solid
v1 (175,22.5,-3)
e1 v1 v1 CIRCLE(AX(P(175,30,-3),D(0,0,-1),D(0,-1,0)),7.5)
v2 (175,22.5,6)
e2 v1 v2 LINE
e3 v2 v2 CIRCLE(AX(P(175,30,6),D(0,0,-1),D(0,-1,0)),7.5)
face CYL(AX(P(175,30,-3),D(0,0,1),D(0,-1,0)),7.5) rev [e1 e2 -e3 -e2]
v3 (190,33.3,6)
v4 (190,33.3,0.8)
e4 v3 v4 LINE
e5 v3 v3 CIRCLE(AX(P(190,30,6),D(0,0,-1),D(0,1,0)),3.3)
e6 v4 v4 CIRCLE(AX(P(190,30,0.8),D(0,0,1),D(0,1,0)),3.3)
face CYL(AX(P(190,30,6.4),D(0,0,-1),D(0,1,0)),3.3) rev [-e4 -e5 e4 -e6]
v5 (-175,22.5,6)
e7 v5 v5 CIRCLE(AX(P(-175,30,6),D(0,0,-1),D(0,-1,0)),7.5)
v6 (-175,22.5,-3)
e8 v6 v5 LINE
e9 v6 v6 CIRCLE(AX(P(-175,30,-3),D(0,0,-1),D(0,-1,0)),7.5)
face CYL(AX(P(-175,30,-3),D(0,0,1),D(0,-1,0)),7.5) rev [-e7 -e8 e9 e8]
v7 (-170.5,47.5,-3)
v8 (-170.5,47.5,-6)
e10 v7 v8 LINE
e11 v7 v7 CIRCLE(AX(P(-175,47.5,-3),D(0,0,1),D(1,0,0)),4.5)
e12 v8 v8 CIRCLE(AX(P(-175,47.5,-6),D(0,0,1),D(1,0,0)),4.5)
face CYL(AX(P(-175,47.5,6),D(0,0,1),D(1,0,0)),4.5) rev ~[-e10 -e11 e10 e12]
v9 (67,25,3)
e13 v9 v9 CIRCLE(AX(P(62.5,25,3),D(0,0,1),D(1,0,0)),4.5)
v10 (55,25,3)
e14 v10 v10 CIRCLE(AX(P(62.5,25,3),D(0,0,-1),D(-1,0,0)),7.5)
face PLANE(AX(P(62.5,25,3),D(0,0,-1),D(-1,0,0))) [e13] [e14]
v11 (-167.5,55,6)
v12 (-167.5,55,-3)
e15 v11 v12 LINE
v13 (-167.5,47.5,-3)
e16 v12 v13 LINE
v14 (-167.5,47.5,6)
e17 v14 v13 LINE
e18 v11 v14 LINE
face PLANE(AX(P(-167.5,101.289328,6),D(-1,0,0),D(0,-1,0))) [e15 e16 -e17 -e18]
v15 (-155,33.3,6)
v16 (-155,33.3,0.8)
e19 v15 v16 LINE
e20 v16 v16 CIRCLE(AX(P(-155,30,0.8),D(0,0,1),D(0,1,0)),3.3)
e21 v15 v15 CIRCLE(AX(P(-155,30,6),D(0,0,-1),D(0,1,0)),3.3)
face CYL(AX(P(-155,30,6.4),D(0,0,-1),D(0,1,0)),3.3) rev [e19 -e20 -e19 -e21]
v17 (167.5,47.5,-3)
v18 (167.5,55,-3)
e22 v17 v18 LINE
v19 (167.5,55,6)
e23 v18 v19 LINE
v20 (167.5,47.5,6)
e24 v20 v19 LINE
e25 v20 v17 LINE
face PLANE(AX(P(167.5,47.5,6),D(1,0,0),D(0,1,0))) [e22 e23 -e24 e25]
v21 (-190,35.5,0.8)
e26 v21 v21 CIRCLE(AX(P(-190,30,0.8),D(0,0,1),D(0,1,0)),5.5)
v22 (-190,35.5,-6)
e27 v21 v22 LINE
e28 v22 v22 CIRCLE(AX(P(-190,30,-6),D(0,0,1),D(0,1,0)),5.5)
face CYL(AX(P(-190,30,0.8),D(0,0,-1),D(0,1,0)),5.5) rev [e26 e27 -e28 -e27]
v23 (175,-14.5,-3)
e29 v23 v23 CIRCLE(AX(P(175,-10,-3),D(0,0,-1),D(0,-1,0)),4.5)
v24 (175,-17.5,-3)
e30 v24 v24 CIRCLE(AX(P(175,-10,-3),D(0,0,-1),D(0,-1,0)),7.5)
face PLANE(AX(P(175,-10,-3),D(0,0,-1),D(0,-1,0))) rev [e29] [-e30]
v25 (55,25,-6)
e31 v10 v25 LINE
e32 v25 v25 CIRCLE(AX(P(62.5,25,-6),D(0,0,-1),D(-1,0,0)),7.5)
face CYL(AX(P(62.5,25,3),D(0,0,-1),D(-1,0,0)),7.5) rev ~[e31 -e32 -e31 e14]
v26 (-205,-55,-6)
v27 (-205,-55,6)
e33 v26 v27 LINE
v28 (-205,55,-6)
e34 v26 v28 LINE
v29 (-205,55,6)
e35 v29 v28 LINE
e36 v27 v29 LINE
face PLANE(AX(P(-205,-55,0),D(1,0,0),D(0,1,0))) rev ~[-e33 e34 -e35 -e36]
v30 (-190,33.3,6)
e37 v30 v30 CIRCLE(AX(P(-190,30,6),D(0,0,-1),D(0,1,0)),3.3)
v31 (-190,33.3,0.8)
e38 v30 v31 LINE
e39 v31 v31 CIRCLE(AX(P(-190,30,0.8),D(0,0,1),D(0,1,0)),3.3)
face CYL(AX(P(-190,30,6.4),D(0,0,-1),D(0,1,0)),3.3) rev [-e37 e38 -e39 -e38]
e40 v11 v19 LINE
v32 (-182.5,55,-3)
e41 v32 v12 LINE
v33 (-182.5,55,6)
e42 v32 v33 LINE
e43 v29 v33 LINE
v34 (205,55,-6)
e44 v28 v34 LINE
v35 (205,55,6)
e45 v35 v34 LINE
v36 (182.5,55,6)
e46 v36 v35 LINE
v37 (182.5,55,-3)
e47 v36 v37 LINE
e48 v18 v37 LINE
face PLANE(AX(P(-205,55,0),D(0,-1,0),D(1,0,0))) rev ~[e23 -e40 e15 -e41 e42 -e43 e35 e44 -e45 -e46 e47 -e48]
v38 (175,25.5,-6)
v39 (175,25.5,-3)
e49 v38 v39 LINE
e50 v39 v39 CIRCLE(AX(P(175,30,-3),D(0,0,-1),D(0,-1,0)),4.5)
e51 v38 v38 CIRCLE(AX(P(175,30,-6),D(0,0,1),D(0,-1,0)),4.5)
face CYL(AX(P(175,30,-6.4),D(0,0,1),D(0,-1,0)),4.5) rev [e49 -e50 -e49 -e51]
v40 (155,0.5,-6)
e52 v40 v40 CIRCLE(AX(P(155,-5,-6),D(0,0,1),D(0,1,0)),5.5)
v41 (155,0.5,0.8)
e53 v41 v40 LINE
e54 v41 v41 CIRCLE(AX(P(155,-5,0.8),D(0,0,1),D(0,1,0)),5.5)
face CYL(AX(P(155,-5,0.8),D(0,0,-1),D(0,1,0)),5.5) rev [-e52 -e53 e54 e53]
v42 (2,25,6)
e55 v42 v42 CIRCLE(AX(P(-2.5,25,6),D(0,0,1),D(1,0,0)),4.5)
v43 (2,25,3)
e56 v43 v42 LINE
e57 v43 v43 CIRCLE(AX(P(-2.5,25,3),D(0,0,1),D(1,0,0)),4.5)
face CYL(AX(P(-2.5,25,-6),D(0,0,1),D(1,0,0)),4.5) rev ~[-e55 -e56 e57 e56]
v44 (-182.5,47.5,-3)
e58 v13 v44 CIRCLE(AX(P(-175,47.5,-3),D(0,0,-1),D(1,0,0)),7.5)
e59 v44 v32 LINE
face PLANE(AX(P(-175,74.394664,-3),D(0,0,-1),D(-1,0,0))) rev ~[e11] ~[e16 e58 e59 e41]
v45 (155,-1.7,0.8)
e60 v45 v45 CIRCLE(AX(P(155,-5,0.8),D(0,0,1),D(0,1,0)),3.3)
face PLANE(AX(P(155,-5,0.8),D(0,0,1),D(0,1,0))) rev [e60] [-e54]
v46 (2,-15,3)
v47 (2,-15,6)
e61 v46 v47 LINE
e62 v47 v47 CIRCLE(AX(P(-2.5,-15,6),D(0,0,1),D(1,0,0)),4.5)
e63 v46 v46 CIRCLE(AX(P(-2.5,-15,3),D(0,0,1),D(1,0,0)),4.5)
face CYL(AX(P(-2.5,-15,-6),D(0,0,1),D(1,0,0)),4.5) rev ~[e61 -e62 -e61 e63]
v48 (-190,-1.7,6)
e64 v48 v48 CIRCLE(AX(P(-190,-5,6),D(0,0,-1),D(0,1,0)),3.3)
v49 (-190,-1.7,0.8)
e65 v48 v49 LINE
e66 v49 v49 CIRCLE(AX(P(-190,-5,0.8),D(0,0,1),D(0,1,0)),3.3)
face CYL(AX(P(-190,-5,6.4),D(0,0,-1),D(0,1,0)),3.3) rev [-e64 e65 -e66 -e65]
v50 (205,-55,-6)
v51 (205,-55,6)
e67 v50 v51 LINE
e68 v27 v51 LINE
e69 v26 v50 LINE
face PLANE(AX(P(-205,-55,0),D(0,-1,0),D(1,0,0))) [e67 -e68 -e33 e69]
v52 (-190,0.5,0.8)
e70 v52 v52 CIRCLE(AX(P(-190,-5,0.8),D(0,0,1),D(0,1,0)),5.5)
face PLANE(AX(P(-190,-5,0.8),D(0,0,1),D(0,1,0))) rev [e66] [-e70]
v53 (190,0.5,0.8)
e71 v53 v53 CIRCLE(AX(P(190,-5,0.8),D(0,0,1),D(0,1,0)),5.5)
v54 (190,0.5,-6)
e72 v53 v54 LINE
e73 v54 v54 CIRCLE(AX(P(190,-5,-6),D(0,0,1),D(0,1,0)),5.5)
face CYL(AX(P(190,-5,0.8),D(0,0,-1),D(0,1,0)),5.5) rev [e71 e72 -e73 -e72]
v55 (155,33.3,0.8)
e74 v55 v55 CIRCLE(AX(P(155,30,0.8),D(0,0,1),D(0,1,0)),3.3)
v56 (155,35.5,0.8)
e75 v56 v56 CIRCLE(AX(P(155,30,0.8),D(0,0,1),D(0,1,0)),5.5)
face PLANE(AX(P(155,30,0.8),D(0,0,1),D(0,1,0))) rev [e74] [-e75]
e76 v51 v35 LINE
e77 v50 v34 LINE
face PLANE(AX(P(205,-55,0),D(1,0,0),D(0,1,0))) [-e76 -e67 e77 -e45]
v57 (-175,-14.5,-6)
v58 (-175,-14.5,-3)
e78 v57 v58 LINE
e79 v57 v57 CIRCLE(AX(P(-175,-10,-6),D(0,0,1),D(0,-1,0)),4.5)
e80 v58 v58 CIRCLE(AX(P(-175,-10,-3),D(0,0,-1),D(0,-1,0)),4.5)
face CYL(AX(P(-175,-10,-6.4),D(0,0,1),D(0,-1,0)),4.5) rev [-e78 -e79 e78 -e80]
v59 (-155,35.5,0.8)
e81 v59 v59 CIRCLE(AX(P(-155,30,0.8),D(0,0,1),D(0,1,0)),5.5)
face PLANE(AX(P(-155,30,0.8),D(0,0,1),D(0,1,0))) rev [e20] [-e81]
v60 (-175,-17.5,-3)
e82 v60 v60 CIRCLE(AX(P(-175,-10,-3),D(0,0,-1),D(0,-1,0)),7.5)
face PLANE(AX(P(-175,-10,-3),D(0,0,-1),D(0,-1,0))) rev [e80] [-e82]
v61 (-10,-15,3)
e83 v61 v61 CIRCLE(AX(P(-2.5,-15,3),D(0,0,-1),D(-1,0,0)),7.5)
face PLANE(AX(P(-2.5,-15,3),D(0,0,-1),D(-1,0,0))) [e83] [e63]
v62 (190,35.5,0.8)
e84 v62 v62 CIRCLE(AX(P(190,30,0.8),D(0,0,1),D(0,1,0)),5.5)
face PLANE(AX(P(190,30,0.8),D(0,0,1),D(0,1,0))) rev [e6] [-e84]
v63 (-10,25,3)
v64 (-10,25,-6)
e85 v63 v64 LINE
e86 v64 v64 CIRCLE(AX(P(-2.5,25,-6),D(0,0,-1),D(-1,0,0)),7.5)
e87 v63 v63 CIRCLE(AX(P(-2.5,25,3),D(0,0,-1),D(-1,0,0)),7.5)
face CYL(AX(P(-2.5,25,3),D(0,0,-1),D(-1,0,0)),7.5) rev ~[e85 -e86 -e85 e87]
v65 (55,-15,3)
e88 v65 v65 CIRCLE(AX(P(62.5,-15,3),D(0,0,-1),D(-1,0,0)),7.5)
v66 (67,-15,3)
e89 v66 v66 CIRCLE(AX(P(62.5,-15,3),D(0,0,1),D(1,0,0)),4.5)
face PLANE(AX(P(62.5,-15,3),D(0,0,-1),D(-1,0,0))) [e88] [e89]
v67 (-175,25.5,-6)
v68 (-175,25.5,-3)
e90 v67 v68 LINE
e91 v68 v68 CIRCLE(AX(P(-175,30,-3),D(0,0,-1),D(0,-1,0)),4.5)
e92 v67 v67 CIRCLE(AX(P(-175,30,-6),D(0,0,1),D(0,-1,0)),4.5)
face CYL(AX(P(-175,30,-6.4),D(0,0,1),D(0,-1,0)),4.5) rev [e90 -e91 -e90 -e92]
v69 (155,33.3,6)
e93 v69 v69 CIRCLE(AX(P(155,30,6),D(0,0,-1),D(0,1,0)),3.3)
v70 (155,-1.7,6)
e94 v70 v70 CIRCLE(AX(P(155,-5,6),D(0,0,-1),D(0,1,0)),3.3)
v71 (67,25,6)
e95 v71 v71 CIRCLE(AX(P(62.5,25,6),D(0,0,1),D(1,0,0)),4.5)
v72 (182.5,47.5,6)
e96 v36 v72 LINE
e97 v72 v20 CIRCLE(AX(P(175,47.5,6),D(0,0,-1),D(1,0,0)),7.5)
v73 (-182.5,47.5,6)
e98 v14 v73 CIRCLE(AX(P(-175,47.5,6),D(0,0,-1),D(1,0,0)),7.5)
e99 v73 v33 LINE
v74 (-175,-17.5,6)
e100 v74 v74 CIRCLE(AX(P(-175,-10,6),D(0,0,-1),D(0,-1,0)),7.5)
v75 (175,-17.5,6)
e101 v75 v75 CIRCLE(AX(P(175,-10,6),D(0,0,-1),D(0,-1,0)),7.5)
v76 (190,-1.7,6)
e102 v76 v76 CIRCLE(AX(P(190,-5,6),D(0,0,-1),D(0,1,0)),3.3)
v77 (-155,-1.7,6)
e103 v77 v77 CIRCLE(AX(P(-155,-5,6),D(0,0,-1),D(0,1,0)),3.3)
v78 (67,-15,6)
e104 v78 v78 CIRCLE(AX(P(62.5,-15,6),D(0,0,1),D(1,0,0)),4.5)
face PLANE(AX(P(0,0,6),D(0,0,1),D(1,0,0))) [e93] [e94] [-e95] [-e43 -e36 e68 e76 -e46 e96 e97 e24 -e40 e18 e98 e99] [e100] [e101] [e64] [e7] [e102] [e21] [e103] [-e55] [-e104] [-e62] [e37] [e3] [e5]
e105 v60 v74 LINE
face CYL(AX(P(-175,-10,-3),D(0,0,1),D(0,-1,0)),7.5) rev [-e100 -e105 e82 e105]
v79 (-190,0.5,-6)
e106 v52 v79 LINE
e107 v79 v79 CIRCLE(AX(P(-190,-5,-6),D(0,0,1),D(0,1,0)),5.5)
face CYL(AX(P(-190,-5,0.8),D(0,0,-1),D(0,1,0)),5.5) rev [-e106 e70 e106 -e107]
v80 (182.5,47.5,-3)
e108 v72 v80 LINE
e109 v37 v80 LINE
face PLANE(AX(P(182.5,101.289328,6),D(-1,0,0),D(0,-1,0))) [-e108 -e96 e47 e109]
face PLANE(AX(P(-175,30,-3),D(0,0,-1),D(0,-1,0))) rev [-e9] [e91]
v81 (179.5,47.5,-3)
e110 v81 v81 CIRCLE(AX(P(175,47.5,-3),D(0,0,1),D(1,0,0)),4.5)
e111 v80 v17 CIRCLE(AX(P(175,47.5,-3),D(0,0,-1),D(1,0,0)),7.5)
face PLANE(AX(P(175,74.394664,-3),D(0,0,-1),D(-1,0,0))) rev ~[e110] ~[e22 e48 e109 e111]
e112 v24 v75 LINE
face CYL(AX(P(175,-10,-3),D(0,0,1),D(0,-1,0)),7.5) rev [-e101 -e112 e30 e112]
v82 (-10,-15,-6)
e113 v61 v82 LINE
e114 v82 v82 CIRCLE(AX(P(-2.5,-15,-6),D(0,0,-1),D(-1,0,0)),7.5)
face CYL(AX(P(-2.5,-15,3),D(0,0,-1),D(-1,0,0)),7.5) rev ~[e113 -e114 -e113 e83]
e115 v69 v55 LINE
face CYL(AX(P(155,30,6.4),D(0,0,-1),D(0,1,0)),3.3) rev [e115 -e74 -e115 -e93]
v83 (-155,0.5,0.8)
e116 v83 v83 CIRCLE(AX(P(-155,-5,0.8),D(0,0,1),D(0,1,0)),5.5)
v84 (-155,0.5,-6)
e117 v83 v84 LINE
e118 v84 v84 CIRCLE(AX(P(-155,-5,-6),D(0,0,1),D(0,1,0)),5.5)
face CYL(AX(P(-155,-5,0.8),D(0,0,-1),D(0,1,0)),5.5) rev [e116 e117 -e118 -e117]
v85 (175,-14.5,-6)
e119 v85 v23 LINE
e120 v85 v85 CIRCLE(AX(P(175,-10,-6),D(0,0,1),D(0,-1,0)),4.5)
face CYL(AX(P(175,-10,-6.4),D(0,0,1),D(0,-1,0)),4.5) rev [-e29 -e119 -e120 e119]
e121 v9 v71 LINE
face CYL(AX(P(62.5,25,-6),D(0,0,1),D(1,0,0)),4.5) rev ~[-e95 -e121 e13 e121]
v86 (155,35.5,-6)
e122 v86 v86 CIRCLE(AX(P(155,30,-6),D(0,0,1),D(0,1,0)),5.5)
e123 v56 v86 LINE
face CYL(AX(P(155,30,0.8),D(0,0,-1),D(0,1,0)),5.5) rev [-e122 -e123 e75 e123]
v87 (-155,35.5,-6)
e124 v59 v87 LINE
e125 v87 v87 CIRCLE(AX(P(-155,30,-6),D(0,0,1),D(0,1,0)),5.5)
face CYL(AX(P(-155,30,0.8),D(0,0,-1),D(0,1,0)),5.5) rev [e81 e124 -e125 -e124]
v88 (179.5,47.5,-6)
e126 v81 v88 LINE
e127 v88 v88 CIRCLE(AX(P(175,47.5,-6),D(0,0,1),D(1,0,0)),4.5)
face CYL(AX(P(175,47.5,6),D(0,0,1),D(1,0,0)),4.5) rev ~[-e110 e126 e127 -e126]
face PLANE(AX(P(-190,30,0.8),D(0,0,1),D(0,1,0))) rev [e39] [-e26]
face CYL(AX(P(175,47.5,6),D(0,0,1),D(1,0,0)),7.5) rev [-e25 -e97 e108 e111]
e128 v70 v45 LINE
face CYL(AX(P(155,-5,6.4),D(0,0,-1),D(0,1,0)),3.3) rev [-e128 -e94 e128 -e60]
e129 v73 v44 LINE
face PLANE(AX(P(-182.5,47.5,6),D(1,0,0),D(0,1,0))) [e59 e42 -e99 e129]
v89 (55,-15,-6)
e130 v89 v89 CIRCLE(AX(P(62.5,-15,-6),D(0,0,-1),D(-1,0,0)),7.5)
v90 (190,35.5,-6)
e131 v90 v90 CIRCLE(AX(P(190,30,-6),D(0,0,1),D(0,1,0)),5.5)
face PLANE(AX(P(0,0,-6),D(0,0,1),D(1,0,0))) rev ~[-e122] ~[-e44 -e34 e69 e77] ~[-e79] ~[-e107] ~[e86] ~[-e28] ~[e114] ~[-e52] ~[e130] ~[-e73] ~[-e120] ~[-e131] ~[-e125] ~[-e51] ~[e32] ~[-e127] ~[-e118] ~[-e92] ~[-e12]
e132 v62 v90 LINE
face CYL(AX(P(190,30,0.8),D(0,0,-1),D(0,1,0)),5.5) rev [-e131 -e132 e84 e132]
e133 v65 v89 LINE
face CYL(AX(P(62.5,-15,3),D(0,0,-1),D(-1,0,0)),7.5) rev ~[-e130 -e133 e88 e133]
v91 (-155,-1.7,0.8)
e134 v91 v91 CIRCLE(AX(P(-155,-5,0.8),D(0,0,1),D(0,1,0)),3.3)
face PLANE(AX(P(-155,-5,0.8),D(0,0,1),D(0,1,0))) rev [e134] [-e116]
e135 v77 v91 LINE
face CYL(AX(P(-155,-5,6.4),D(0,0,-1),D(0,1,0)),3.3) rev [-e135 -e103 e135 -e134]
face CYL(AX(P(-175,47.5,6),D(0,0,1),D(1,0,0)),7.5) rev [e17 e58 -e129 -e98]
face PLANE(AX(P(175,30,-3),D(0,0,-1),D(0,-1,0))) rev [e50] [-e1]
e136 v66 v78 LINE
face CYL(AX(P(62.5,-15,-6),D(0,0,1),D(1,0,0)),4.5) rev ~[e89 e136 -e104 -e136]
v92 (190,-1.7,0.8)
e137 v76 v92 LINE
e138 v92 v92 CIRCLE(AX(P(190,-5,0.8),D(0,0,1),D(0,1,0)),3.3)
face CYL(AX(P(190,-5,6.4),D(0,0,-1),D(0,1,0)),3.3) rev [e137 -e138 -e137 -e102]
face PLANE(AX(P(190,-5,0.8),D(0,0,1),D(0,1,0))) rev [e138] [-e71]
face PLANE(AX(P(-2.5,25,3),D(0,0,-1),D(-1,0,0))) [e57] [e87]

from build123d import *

# Parameters (mm, degrees)
SKETCH_1_W                 = 410
SKETCH_1_H                 = 110
EXTRUDE_1_DEPTH            = 6
HOLE_WIZARD_3_AT_2_COUNT   = 2
HOLE_WIZARD_3_AT_2_PITCH   = 35
HOLE_WIZARD_3_AT_3_COUNT   = 2
HOLE_WIZARD_3_AT_3_PITCH   = 35
HOLE_WIZARD_3_AT_4_COUNT   = 2
HOLE_WIZARD_3_AT_4_PITCH   = 49.497474683
PATTERN_LINEAR_1_COUNT     = 2
PATTERN_LINEAR_1_PITCH     = 345
HOLE_WIZARD_2_D            = 9
HOLE_WIZARD_2_DEPTH        = 12.4
HOLE_WIZARD_2_CBORE_D      = 15
HOLE_WIZARD_2_CBORE_DEPTH  = 9
HOLE_WIZARD_2_TIP          = 2.703872786
HOLE_WIZARD_3_2_AT_2_COUNT = 2
HOLE_WIZARD_3_2_AT_2_PITCH = 40
SKETCH_14_R                = 4.5
CUT_EXTRUDE_1_DEPTH        = 213.588804973
CUT_EXTRUDE_2_DEPTH        = 9
PATTERN_LINEAR_2_COUNT     = 2
PATTERN_LINEAR_2_PITCH     = 350


with BuildPart() as part:
    # 草图1 → 凸台-拉伸1 (new, symmetric)
    with BuildSketch(Plane.XY):
        Rectangle(SKETCH_1_W, SKETCH_1_H)
    extrude(amount=EXTRUDE_1_DEPTH, both=True)

    # 草图3 → Hole Wizard 3 (revolve, cut)
    with BuildSketch(Plane(origin=(190, 30, -6), x_dir=(0, 1, 0), z_dir=(1, 0, 0))):
        Polygon((0, 0), (0, 14.382840043), (3.3, 12.4), (3.3, 6.8), (5.5, 6.8), (5.5, 0), align=None)
    hole_wizard_3 = revolve(axis=Axis((190, 30, -12.35), (0, 0, 1)), mode=Mode.SUBTRACT)

    # Hole Wizard 3 at 2: Hole Wizard 3 ×2
    with Locations(*[(-i * HOLE_WIZARD_3_AT_2_PITCH, 0, 0) for i in range(1, HOLE_WIZARD_3_AT_2_COUNT)]):
        add(hole_wizard_3, mode=Mode.SUBTRACT)

    # Hole Wizard 3 at 3: Hole Wizard 3 ×2
    with Locations(*[(0, -i * HOLE_WIZARD_3_AT_3_PITCH, 0) for i in range(1, HOLE_WIZARD_3_AT_3_COUNT)]):
        add(hole_wizard_3, mode=Mode.SUBTRACT)

    # Hole Wizard 3 at 4: Hole Wizard 3 ×2
    with Locations(*[Vector(-0.7071067811865477, -0.7071067811865474, 0) * (i * HOLE_WIZARD_3_AT_4_PITCH) for i in range(1, HOLE_WIZARD_3_AT_4_COUNT)]):
        add(hole_wizard_3, mode=Mode.SUBTRACT)

    # 阵列(线性)1: Hole Wizard 3 ×2
    with Locations(*[(-i * PATTERN_LINEAR_1_PITCH, 0, 0) for i in range(1, PATTERN_LINEAR_1_COUNT)]):
        add(hole_wizard_3, mode=Mode.SUBTRACT)

    # 阵列(线性)1 copy 1 sketch → 阵列(线性)1 copy 1 (revolve, cut)
    with BuildSketch(Plane(origin=(-190, 30, -6), x_dir=(0, 1, 0), z_dir=(1, 0, 0))):
        Polygon((0, 0), (0, 14.382840043), (3.3, 12.4), (3.3, 6.8), (5.5, 6.8), (5.5, 0), align=None)
    revolve(axis=Axis((-190, 30, -12.35), (0, 0, 1)), mode=Mode.SUBTRACT)

    # 阵列(线性)1 copy 2 sketch → 阵列(线性)1 copy 2 (revolve, cut)
    with BuildSketch(Plane(origin=(-155, -5, -6), x_dir=(0, 1, 0), z_dir=(1, 0, 0))):
        Polygon((0, 0), (0, 14.382840043), (3.3, 12.4), (3.3, 6.8), (5.5, 6.8), (5.5, 0), align=None)
    revolve(axis=Axis((-155, -5, -12.35), (0, 0, 1)), mode=Mode.SUBTRACT)

    # 阵列(线性)1 copy 3 sketch → 阵列(线性)1 copy 3 (revolve, cut)
    with BuildSketch(Plane(origin=(-190, -5, -6), x_dir=(0, 1, 0), z_dir=(1, 0, 0))):
        Polygon((0, 0), (0, 14.382840043), (3.3, 12.4), (3.3, 6.8), (5.5, 6.8), (5.5, 0), align=None)
    revolve(axis=Axis((-190, -5, -12.35), (0, 0, 1)), mode=Mode.SUBTRACT)

    # 打孔尺寸(%根据)内六角圆柱头螺钉的类型2
    with Locations(Plane(origin=(62.5, 25, -6), x_dir=(-1, 0, 0), z_dir=(0, 0, -1))):
        with Locations((0, 0), (0, -40), (65, -40), (65, 0)):
            CounterBoreHole(HOLE_WIZARD_2_D / 2, HOLE_WIZARD_2_CBORE_D / 2, HOLE_WIZARD_2_CBORE_DEPTH, depth=HOLE_WIZARD_2_DEPTH)
            with Locations((0, 0, -(HOLE_WIZARD_2_DEPTH + HOLE_WIZARD_2_TIP / 2))):  # 118° drill point
                Cone(0, HOLE_WIZARD_2_D / 2, HOLE_WIZARD_2_TIP, mode=Mode.SUBTRACT)

    # 草图5 → Hole Wizard 3 2 (revolve, cut)
    with BuildSketch(Plane(origin=(-175, 30, 6), x_dir=(0, -1, 0), z_dir=(1, 0, 0))):
        Polygon((0, 0), (0, 15.103872786), (4.5, 12.4), (4.5, 9), (7.5, 9), (7.5, 0), align=None)
    hole_wizard_3_2 = revolve(axis=Axis((-175, 30, 12.35), (0, 0, -1)), mode=Mode.SUBTRACT)

    # Hole Wizard 3 2 at 2: Hole Wizard 3 2 ×2
    with Locations(*[(0, -i * HOLE_WIZARD_3_2_AT_2_PITCH, 0) for i in range(1, HOLE_WIZARD_3_2_AT_2_COUNT)]):
        add(hole_wizard_3_2, mode=Mode.SUBTRACT)

    # 草图14 → 切除-拉伸1 (cut, through all)
    with BuildSketch(Plane.XY.offset(6)):
        with Locations((-175, 47.5)):
            Circle(SKETCH_14_R)
    cut_extrude_1 = extrude(amount=-CUT_EXTRUDE_1_DEPTH, mode=Mode.SUBTRACT)

    # 草图15 → 切除-拉伸2 (cut)
    with BuildSketch(Plane.XY.offset(6)):
        with BuildLine():
            Line((-182.5, 47.5), (-182.5, 101.28932806))
            ThreePointArc((-182.5, 101.28932806), (-175, 108.78932806), (-167.5, 101.28932806))
            Line((-167.5, 101.28932806), (-167.5, 47.5))
            ThreePointArc((-167.5, 47.5), (-175, 40), (-182.5, 47.5))
        make_face()
    cut_extrude_2 = extrude(amount=-CUT_EXTRUDE_2_DEPTH, mode=Mode.SUBTRACT)

    # 阵列(线性)2: Hole Wizard 3 2, 切除-拉伸1, 切除-拉伸2 ×2
    with Locations(*[(i * PATTERN_LINEAR_2_PITCH, 0, 0) for i in range(1, PATTERN_LINEAR_2_COUNT)]):
        add(hole_wizard_3_2, mode=Mode.SUBTRACT)
        add(cut_extrude_1, mode=Mode.SUBTRACT)
        add(cut_extrude_2, mode=Mode.SUBTRACT)

    # 阵列(线性)2 copy 1 sketch → 阵列(线性)2 copy 1 (revolve, cut)
    with BuildSketch(Plane(origin=(175, -10, 6), x_dir=(0, -1, 0), z_dir=(1, 0, 0))):
        Polygon((0, 0), (0, 15.103872786), (4.5, 12.4), (4.5, 9), (7.5, 9), (7.5, 0), align=None)
    revolve(axis=Axis((175, -10, 12.35), (0, 0, -1)), mode=Mode.SUBTRACT)


solid = part.part
